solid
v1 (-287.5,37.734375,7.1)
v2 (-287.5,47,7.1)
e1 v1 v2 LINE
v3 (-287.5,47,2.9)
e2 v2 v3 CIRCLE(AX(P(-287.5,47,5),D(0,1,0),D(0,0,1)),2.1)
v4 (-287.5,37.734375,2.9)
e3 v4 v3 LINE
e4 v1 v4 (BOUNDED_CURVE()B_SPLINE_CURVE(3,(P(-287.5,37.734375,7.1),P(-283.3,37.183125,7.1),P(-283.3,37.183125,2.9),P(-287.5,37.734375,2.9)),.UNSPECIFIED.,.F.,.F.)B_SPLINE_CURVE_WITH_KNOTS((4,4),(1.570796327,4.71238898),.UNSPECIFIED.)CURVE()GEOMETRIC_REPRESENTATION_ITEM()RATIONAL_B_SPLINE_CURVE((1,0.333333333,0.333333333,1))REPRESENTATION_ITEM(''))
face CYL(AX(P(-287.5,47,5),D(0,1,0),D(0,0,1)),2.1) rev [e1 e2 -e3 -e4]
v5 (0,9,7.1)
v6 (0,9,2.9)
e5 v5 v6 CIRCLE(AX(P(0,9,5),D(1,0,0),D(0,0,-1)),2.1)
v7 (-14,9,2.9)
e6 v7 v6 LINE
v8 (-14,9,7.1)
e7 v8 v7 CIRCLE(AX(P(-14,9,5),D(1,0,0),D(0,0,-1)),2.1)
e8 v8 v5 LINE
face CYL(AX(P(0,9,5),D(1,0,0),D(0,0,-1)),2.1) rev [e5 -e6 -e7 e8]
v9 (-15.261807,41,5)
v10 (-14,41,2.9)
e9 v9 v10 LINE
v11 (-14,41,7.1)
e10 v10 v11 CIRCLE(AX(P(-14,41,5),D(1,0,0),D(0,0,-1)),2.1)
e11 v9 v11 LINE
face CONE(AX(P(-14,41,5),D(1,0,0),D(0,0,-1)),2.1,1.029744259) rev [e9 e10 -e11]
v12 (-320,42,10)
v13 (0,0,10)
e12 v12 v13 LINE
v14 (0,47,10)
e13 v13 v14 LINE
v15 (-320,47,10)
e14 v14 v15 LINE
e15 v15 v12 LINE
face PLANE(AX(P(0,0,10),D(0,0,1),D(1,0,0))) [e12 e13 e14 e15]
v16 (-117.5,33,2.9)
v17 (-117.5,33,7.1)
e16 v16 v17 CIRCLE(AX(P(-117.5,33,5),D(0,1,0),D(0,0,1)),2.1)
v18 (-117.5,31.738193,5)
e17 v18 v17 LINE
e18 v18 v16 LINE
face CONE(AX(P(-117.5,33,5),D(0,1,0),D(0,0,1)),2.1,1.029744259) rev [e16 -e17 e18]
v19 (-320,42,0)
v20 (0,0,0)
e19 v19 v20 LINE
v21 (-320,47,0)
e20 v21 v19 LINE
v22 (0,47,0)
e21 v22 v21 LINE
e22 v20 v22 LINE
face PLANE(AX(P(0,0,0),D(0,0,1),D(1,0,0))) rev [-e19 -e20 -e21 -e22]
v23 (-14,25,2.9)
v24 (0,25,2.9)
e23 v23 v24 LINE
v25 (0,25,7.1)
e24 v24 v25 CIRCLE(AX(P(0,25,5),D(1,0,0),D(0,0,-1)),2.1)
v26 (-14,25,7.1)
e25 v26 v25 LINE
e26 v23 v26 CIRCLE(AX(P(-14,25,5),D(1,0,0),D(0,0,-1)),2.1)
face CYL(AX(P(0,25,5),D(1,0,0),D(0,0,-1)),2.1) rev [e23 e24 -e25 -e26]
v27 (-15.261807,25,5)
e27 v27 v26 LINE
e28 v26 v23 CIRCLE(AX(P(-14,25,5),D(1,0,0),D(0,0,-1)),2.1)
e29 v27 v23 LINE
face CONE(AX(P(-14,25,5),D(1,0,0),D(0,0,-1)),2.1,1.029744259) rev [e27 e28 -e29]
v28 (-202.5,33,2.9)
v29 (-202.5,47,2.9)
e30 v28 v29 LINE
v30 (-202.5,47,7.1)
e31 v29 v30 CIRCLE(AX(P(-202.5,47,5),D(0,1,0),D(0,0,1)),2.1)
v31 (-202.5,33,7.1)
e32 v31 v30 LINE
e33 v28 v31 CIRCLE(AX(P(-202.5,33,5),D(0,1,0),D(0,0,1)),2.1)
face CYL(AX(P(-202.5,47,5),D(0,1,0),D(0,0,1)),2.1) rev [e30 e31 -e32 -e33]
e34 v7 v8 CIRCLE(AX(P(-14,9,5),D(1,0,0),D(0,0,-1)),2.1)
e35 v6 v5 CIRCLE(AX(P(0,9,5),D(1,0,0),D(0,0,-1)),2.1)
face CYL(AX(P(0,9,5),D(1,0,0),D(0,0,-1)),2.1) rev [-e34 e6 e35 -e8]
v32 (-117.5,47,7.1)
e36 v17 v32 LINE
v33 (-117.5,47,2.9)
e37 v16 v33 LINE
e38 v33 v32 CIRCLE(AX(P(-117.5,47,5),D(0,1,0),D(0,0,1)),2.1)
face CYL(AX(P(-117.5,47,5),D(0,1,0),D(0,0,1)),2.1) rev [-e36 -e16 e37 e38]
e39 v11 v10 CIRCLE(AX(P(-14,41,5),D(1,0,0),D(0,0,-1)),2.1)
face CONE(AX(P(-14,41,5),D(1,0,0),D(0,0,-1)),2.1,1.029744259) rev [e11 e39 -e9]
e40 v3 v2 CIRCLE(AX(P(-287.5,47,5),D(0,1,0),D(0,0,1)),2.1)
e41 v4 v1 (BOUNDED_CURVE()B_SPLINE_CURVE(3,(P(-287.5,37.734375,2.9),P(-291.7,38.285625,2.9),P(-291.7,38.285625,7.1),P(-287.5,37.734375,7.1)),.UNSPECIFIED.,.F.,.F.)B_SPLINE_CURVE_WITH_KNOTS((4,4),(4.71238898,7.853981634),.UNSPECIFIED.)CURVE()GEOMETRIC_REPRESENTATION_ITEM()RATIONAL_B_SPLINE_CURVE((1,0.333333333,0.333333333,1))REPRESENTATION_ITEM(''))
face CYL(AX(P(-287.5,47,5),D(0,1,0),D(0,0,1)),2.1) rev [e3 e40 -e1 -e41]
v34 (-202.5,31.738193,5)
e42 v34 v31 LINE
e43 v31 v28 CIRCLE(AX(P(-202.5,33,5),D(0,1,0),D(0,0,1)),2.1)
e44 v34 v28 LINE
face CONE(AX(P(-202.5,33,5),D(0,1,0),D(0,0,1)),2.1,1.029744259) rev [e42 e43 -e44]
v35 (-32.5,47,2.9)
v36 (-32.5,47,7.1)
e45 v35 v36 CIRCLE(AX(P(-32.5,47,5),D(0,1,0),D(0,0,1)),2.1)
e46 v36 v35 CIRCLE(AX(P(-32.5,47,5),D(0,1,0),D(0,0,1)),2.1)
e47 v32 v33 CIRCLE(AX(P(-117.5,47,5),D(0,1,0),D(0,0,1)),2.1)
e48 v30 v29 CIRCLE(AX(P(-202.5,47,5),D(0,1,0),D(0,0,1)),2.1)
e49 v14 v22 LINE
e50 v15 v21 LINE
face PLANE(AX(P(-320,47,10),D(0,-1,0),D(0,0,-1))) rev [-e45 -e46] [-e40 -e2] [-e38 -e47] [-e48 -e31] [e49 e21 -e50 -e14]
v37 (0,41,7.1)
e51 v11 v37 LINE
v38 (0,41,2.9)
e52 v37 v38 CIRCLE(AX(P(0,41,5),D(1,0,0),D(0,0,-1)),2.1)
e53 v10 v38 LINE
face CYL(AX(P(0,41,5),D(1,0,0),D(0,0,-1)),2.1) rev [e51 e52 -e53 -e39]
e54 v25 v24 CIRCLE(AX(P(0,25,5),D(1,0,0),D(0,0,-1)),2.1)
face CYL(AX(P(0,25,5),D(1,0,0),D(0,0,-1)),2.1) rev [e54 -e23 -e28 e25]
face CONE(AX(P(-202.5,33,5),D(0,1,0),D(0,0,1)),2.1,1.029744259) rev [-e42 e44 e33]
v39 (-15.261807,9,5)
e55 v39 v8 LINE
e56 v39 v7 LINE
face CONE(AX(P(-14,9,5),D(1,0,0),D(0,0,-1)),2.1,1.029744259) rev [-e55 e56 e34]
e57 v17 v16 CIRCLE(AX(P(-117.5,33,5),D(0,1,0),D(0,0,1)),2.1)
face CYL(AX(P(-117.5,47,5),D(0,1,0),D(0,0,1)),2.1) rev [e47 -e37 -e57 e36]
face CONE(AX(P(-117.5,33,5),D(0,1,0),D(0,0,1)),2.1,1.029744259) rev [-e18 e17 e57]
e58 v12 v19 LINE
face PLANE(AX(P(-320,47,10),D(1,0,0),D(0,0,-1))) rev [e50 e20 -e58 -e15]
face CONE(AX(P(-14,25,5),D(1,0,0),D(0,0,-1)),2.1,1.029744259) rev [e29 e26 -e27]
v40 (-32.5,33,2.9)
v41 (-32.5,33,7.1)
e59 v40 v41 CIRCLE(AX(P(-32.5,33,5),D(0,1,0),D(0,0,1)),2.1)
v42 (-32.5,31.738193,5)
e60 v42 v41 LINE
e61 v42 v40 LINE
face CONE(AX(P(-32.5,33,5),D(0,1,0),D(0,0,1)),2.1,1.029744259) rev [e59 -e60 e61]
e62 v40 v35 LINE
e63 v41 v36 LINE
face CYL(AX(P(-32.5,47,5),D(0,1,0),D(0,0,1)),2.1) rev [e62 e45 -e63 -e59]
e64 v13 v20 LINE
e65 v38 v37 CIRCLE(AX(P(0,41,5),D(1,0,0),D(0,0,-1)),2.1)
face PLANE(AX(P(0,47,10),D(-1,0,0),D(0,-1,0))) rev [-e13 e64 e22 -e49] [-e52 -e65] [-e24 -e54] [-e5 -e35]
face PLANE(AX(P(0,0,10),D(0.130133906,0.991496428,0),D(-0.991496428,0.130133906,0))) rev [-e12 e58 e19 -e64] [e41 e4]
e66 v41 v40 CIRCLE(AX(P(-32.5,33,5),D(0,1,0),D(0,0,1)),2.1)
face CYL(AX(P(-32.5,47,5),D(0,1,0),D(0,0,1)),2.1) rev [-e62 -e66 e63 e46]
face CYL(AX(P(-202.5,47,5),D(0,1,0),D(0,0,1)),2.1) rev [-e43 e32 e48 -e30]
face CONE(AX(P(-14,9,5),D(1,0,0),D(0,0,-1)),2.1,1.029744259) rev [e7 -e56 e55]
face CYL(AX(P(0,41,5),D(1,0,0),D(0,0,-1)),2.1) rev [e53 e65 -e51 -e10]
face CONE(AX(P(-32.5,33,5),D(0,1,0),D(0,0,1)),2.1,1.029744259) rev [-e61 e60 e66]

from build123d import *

# Parameters (mm, degrees)
BOSS_EXTRUDE1_DEPTH   = 10
M5_TAPPED_HOLE1_D     = 4.2
M5_TAPPED_HOLE1_DEPTH = 14
M5_TAPPED_HOLE1_TIP   = 1.2618073
M5_TAPPED_HOLE2_D     = 4.2
M5_TAPPED_HOLE2_DEPTH = 14
M5_TAPPED_HOLE2_TIP   = 1.2618073


with BuildPart() as part:
    # Sketch1 → Boss-Extrude1 (new body)
    with BuildSketch(Plane.XY):
        Polygon((0, 0), (-320, 42), (-320, 47), (0, 47), align=None)
    extrude(amount=BOSS_EXTRUDE1_DEPTH)

    # M5 Tapped Hole1
    with Locations(Plane(origin=(0, 47, 0), x_dir=(-1, 0, 0), z_dir=(0, 1, 0))):
        with Locations((287.5, 5), (202.5, 5), (117.5, 5), (32.5, 5)):
            Hole(M5_TAPPED_HOLE1_D / 2, depth=M5_TAPPED_HOLE1_DEPTH)
            with Locations((0, 0, -(M5_TAPPED_HOLE1_DEPTH + M5_TAPPED_HOLE1_TIP / 2))):  # 118° drill point
                Cone(0, M5_TAPPED_HOLE1_D / 2, M5_TAPPED_HOLE1_TIP, mode=Mode.SUBTRACT)

    # M5 Tapped Hole2
    with Locations(Plane(origin=(0, 0, 0), x_dir=(0, 0, -1), z_dir=(1, 0, 0))):
        with Locations((-5, 41), (-5, 25), (-5, 9)):
            Hole(M5_TAPPED_HOLE2_D / 2, depth=M5_TAPPED_HOLE2_DEPTH)
            with Locations((0, 0, -(M5_TAPPED_HOLE2_DEPTH + M5_TAPPED_HOLE2_TIP / 2))):  # 118° drill point
                Cone(0, M5_TAPPED_HOLE2_D / 2, M5_TAPPED_HOLE2_TIP, mode=Mode.SUBTRACT)


solid = part.part
